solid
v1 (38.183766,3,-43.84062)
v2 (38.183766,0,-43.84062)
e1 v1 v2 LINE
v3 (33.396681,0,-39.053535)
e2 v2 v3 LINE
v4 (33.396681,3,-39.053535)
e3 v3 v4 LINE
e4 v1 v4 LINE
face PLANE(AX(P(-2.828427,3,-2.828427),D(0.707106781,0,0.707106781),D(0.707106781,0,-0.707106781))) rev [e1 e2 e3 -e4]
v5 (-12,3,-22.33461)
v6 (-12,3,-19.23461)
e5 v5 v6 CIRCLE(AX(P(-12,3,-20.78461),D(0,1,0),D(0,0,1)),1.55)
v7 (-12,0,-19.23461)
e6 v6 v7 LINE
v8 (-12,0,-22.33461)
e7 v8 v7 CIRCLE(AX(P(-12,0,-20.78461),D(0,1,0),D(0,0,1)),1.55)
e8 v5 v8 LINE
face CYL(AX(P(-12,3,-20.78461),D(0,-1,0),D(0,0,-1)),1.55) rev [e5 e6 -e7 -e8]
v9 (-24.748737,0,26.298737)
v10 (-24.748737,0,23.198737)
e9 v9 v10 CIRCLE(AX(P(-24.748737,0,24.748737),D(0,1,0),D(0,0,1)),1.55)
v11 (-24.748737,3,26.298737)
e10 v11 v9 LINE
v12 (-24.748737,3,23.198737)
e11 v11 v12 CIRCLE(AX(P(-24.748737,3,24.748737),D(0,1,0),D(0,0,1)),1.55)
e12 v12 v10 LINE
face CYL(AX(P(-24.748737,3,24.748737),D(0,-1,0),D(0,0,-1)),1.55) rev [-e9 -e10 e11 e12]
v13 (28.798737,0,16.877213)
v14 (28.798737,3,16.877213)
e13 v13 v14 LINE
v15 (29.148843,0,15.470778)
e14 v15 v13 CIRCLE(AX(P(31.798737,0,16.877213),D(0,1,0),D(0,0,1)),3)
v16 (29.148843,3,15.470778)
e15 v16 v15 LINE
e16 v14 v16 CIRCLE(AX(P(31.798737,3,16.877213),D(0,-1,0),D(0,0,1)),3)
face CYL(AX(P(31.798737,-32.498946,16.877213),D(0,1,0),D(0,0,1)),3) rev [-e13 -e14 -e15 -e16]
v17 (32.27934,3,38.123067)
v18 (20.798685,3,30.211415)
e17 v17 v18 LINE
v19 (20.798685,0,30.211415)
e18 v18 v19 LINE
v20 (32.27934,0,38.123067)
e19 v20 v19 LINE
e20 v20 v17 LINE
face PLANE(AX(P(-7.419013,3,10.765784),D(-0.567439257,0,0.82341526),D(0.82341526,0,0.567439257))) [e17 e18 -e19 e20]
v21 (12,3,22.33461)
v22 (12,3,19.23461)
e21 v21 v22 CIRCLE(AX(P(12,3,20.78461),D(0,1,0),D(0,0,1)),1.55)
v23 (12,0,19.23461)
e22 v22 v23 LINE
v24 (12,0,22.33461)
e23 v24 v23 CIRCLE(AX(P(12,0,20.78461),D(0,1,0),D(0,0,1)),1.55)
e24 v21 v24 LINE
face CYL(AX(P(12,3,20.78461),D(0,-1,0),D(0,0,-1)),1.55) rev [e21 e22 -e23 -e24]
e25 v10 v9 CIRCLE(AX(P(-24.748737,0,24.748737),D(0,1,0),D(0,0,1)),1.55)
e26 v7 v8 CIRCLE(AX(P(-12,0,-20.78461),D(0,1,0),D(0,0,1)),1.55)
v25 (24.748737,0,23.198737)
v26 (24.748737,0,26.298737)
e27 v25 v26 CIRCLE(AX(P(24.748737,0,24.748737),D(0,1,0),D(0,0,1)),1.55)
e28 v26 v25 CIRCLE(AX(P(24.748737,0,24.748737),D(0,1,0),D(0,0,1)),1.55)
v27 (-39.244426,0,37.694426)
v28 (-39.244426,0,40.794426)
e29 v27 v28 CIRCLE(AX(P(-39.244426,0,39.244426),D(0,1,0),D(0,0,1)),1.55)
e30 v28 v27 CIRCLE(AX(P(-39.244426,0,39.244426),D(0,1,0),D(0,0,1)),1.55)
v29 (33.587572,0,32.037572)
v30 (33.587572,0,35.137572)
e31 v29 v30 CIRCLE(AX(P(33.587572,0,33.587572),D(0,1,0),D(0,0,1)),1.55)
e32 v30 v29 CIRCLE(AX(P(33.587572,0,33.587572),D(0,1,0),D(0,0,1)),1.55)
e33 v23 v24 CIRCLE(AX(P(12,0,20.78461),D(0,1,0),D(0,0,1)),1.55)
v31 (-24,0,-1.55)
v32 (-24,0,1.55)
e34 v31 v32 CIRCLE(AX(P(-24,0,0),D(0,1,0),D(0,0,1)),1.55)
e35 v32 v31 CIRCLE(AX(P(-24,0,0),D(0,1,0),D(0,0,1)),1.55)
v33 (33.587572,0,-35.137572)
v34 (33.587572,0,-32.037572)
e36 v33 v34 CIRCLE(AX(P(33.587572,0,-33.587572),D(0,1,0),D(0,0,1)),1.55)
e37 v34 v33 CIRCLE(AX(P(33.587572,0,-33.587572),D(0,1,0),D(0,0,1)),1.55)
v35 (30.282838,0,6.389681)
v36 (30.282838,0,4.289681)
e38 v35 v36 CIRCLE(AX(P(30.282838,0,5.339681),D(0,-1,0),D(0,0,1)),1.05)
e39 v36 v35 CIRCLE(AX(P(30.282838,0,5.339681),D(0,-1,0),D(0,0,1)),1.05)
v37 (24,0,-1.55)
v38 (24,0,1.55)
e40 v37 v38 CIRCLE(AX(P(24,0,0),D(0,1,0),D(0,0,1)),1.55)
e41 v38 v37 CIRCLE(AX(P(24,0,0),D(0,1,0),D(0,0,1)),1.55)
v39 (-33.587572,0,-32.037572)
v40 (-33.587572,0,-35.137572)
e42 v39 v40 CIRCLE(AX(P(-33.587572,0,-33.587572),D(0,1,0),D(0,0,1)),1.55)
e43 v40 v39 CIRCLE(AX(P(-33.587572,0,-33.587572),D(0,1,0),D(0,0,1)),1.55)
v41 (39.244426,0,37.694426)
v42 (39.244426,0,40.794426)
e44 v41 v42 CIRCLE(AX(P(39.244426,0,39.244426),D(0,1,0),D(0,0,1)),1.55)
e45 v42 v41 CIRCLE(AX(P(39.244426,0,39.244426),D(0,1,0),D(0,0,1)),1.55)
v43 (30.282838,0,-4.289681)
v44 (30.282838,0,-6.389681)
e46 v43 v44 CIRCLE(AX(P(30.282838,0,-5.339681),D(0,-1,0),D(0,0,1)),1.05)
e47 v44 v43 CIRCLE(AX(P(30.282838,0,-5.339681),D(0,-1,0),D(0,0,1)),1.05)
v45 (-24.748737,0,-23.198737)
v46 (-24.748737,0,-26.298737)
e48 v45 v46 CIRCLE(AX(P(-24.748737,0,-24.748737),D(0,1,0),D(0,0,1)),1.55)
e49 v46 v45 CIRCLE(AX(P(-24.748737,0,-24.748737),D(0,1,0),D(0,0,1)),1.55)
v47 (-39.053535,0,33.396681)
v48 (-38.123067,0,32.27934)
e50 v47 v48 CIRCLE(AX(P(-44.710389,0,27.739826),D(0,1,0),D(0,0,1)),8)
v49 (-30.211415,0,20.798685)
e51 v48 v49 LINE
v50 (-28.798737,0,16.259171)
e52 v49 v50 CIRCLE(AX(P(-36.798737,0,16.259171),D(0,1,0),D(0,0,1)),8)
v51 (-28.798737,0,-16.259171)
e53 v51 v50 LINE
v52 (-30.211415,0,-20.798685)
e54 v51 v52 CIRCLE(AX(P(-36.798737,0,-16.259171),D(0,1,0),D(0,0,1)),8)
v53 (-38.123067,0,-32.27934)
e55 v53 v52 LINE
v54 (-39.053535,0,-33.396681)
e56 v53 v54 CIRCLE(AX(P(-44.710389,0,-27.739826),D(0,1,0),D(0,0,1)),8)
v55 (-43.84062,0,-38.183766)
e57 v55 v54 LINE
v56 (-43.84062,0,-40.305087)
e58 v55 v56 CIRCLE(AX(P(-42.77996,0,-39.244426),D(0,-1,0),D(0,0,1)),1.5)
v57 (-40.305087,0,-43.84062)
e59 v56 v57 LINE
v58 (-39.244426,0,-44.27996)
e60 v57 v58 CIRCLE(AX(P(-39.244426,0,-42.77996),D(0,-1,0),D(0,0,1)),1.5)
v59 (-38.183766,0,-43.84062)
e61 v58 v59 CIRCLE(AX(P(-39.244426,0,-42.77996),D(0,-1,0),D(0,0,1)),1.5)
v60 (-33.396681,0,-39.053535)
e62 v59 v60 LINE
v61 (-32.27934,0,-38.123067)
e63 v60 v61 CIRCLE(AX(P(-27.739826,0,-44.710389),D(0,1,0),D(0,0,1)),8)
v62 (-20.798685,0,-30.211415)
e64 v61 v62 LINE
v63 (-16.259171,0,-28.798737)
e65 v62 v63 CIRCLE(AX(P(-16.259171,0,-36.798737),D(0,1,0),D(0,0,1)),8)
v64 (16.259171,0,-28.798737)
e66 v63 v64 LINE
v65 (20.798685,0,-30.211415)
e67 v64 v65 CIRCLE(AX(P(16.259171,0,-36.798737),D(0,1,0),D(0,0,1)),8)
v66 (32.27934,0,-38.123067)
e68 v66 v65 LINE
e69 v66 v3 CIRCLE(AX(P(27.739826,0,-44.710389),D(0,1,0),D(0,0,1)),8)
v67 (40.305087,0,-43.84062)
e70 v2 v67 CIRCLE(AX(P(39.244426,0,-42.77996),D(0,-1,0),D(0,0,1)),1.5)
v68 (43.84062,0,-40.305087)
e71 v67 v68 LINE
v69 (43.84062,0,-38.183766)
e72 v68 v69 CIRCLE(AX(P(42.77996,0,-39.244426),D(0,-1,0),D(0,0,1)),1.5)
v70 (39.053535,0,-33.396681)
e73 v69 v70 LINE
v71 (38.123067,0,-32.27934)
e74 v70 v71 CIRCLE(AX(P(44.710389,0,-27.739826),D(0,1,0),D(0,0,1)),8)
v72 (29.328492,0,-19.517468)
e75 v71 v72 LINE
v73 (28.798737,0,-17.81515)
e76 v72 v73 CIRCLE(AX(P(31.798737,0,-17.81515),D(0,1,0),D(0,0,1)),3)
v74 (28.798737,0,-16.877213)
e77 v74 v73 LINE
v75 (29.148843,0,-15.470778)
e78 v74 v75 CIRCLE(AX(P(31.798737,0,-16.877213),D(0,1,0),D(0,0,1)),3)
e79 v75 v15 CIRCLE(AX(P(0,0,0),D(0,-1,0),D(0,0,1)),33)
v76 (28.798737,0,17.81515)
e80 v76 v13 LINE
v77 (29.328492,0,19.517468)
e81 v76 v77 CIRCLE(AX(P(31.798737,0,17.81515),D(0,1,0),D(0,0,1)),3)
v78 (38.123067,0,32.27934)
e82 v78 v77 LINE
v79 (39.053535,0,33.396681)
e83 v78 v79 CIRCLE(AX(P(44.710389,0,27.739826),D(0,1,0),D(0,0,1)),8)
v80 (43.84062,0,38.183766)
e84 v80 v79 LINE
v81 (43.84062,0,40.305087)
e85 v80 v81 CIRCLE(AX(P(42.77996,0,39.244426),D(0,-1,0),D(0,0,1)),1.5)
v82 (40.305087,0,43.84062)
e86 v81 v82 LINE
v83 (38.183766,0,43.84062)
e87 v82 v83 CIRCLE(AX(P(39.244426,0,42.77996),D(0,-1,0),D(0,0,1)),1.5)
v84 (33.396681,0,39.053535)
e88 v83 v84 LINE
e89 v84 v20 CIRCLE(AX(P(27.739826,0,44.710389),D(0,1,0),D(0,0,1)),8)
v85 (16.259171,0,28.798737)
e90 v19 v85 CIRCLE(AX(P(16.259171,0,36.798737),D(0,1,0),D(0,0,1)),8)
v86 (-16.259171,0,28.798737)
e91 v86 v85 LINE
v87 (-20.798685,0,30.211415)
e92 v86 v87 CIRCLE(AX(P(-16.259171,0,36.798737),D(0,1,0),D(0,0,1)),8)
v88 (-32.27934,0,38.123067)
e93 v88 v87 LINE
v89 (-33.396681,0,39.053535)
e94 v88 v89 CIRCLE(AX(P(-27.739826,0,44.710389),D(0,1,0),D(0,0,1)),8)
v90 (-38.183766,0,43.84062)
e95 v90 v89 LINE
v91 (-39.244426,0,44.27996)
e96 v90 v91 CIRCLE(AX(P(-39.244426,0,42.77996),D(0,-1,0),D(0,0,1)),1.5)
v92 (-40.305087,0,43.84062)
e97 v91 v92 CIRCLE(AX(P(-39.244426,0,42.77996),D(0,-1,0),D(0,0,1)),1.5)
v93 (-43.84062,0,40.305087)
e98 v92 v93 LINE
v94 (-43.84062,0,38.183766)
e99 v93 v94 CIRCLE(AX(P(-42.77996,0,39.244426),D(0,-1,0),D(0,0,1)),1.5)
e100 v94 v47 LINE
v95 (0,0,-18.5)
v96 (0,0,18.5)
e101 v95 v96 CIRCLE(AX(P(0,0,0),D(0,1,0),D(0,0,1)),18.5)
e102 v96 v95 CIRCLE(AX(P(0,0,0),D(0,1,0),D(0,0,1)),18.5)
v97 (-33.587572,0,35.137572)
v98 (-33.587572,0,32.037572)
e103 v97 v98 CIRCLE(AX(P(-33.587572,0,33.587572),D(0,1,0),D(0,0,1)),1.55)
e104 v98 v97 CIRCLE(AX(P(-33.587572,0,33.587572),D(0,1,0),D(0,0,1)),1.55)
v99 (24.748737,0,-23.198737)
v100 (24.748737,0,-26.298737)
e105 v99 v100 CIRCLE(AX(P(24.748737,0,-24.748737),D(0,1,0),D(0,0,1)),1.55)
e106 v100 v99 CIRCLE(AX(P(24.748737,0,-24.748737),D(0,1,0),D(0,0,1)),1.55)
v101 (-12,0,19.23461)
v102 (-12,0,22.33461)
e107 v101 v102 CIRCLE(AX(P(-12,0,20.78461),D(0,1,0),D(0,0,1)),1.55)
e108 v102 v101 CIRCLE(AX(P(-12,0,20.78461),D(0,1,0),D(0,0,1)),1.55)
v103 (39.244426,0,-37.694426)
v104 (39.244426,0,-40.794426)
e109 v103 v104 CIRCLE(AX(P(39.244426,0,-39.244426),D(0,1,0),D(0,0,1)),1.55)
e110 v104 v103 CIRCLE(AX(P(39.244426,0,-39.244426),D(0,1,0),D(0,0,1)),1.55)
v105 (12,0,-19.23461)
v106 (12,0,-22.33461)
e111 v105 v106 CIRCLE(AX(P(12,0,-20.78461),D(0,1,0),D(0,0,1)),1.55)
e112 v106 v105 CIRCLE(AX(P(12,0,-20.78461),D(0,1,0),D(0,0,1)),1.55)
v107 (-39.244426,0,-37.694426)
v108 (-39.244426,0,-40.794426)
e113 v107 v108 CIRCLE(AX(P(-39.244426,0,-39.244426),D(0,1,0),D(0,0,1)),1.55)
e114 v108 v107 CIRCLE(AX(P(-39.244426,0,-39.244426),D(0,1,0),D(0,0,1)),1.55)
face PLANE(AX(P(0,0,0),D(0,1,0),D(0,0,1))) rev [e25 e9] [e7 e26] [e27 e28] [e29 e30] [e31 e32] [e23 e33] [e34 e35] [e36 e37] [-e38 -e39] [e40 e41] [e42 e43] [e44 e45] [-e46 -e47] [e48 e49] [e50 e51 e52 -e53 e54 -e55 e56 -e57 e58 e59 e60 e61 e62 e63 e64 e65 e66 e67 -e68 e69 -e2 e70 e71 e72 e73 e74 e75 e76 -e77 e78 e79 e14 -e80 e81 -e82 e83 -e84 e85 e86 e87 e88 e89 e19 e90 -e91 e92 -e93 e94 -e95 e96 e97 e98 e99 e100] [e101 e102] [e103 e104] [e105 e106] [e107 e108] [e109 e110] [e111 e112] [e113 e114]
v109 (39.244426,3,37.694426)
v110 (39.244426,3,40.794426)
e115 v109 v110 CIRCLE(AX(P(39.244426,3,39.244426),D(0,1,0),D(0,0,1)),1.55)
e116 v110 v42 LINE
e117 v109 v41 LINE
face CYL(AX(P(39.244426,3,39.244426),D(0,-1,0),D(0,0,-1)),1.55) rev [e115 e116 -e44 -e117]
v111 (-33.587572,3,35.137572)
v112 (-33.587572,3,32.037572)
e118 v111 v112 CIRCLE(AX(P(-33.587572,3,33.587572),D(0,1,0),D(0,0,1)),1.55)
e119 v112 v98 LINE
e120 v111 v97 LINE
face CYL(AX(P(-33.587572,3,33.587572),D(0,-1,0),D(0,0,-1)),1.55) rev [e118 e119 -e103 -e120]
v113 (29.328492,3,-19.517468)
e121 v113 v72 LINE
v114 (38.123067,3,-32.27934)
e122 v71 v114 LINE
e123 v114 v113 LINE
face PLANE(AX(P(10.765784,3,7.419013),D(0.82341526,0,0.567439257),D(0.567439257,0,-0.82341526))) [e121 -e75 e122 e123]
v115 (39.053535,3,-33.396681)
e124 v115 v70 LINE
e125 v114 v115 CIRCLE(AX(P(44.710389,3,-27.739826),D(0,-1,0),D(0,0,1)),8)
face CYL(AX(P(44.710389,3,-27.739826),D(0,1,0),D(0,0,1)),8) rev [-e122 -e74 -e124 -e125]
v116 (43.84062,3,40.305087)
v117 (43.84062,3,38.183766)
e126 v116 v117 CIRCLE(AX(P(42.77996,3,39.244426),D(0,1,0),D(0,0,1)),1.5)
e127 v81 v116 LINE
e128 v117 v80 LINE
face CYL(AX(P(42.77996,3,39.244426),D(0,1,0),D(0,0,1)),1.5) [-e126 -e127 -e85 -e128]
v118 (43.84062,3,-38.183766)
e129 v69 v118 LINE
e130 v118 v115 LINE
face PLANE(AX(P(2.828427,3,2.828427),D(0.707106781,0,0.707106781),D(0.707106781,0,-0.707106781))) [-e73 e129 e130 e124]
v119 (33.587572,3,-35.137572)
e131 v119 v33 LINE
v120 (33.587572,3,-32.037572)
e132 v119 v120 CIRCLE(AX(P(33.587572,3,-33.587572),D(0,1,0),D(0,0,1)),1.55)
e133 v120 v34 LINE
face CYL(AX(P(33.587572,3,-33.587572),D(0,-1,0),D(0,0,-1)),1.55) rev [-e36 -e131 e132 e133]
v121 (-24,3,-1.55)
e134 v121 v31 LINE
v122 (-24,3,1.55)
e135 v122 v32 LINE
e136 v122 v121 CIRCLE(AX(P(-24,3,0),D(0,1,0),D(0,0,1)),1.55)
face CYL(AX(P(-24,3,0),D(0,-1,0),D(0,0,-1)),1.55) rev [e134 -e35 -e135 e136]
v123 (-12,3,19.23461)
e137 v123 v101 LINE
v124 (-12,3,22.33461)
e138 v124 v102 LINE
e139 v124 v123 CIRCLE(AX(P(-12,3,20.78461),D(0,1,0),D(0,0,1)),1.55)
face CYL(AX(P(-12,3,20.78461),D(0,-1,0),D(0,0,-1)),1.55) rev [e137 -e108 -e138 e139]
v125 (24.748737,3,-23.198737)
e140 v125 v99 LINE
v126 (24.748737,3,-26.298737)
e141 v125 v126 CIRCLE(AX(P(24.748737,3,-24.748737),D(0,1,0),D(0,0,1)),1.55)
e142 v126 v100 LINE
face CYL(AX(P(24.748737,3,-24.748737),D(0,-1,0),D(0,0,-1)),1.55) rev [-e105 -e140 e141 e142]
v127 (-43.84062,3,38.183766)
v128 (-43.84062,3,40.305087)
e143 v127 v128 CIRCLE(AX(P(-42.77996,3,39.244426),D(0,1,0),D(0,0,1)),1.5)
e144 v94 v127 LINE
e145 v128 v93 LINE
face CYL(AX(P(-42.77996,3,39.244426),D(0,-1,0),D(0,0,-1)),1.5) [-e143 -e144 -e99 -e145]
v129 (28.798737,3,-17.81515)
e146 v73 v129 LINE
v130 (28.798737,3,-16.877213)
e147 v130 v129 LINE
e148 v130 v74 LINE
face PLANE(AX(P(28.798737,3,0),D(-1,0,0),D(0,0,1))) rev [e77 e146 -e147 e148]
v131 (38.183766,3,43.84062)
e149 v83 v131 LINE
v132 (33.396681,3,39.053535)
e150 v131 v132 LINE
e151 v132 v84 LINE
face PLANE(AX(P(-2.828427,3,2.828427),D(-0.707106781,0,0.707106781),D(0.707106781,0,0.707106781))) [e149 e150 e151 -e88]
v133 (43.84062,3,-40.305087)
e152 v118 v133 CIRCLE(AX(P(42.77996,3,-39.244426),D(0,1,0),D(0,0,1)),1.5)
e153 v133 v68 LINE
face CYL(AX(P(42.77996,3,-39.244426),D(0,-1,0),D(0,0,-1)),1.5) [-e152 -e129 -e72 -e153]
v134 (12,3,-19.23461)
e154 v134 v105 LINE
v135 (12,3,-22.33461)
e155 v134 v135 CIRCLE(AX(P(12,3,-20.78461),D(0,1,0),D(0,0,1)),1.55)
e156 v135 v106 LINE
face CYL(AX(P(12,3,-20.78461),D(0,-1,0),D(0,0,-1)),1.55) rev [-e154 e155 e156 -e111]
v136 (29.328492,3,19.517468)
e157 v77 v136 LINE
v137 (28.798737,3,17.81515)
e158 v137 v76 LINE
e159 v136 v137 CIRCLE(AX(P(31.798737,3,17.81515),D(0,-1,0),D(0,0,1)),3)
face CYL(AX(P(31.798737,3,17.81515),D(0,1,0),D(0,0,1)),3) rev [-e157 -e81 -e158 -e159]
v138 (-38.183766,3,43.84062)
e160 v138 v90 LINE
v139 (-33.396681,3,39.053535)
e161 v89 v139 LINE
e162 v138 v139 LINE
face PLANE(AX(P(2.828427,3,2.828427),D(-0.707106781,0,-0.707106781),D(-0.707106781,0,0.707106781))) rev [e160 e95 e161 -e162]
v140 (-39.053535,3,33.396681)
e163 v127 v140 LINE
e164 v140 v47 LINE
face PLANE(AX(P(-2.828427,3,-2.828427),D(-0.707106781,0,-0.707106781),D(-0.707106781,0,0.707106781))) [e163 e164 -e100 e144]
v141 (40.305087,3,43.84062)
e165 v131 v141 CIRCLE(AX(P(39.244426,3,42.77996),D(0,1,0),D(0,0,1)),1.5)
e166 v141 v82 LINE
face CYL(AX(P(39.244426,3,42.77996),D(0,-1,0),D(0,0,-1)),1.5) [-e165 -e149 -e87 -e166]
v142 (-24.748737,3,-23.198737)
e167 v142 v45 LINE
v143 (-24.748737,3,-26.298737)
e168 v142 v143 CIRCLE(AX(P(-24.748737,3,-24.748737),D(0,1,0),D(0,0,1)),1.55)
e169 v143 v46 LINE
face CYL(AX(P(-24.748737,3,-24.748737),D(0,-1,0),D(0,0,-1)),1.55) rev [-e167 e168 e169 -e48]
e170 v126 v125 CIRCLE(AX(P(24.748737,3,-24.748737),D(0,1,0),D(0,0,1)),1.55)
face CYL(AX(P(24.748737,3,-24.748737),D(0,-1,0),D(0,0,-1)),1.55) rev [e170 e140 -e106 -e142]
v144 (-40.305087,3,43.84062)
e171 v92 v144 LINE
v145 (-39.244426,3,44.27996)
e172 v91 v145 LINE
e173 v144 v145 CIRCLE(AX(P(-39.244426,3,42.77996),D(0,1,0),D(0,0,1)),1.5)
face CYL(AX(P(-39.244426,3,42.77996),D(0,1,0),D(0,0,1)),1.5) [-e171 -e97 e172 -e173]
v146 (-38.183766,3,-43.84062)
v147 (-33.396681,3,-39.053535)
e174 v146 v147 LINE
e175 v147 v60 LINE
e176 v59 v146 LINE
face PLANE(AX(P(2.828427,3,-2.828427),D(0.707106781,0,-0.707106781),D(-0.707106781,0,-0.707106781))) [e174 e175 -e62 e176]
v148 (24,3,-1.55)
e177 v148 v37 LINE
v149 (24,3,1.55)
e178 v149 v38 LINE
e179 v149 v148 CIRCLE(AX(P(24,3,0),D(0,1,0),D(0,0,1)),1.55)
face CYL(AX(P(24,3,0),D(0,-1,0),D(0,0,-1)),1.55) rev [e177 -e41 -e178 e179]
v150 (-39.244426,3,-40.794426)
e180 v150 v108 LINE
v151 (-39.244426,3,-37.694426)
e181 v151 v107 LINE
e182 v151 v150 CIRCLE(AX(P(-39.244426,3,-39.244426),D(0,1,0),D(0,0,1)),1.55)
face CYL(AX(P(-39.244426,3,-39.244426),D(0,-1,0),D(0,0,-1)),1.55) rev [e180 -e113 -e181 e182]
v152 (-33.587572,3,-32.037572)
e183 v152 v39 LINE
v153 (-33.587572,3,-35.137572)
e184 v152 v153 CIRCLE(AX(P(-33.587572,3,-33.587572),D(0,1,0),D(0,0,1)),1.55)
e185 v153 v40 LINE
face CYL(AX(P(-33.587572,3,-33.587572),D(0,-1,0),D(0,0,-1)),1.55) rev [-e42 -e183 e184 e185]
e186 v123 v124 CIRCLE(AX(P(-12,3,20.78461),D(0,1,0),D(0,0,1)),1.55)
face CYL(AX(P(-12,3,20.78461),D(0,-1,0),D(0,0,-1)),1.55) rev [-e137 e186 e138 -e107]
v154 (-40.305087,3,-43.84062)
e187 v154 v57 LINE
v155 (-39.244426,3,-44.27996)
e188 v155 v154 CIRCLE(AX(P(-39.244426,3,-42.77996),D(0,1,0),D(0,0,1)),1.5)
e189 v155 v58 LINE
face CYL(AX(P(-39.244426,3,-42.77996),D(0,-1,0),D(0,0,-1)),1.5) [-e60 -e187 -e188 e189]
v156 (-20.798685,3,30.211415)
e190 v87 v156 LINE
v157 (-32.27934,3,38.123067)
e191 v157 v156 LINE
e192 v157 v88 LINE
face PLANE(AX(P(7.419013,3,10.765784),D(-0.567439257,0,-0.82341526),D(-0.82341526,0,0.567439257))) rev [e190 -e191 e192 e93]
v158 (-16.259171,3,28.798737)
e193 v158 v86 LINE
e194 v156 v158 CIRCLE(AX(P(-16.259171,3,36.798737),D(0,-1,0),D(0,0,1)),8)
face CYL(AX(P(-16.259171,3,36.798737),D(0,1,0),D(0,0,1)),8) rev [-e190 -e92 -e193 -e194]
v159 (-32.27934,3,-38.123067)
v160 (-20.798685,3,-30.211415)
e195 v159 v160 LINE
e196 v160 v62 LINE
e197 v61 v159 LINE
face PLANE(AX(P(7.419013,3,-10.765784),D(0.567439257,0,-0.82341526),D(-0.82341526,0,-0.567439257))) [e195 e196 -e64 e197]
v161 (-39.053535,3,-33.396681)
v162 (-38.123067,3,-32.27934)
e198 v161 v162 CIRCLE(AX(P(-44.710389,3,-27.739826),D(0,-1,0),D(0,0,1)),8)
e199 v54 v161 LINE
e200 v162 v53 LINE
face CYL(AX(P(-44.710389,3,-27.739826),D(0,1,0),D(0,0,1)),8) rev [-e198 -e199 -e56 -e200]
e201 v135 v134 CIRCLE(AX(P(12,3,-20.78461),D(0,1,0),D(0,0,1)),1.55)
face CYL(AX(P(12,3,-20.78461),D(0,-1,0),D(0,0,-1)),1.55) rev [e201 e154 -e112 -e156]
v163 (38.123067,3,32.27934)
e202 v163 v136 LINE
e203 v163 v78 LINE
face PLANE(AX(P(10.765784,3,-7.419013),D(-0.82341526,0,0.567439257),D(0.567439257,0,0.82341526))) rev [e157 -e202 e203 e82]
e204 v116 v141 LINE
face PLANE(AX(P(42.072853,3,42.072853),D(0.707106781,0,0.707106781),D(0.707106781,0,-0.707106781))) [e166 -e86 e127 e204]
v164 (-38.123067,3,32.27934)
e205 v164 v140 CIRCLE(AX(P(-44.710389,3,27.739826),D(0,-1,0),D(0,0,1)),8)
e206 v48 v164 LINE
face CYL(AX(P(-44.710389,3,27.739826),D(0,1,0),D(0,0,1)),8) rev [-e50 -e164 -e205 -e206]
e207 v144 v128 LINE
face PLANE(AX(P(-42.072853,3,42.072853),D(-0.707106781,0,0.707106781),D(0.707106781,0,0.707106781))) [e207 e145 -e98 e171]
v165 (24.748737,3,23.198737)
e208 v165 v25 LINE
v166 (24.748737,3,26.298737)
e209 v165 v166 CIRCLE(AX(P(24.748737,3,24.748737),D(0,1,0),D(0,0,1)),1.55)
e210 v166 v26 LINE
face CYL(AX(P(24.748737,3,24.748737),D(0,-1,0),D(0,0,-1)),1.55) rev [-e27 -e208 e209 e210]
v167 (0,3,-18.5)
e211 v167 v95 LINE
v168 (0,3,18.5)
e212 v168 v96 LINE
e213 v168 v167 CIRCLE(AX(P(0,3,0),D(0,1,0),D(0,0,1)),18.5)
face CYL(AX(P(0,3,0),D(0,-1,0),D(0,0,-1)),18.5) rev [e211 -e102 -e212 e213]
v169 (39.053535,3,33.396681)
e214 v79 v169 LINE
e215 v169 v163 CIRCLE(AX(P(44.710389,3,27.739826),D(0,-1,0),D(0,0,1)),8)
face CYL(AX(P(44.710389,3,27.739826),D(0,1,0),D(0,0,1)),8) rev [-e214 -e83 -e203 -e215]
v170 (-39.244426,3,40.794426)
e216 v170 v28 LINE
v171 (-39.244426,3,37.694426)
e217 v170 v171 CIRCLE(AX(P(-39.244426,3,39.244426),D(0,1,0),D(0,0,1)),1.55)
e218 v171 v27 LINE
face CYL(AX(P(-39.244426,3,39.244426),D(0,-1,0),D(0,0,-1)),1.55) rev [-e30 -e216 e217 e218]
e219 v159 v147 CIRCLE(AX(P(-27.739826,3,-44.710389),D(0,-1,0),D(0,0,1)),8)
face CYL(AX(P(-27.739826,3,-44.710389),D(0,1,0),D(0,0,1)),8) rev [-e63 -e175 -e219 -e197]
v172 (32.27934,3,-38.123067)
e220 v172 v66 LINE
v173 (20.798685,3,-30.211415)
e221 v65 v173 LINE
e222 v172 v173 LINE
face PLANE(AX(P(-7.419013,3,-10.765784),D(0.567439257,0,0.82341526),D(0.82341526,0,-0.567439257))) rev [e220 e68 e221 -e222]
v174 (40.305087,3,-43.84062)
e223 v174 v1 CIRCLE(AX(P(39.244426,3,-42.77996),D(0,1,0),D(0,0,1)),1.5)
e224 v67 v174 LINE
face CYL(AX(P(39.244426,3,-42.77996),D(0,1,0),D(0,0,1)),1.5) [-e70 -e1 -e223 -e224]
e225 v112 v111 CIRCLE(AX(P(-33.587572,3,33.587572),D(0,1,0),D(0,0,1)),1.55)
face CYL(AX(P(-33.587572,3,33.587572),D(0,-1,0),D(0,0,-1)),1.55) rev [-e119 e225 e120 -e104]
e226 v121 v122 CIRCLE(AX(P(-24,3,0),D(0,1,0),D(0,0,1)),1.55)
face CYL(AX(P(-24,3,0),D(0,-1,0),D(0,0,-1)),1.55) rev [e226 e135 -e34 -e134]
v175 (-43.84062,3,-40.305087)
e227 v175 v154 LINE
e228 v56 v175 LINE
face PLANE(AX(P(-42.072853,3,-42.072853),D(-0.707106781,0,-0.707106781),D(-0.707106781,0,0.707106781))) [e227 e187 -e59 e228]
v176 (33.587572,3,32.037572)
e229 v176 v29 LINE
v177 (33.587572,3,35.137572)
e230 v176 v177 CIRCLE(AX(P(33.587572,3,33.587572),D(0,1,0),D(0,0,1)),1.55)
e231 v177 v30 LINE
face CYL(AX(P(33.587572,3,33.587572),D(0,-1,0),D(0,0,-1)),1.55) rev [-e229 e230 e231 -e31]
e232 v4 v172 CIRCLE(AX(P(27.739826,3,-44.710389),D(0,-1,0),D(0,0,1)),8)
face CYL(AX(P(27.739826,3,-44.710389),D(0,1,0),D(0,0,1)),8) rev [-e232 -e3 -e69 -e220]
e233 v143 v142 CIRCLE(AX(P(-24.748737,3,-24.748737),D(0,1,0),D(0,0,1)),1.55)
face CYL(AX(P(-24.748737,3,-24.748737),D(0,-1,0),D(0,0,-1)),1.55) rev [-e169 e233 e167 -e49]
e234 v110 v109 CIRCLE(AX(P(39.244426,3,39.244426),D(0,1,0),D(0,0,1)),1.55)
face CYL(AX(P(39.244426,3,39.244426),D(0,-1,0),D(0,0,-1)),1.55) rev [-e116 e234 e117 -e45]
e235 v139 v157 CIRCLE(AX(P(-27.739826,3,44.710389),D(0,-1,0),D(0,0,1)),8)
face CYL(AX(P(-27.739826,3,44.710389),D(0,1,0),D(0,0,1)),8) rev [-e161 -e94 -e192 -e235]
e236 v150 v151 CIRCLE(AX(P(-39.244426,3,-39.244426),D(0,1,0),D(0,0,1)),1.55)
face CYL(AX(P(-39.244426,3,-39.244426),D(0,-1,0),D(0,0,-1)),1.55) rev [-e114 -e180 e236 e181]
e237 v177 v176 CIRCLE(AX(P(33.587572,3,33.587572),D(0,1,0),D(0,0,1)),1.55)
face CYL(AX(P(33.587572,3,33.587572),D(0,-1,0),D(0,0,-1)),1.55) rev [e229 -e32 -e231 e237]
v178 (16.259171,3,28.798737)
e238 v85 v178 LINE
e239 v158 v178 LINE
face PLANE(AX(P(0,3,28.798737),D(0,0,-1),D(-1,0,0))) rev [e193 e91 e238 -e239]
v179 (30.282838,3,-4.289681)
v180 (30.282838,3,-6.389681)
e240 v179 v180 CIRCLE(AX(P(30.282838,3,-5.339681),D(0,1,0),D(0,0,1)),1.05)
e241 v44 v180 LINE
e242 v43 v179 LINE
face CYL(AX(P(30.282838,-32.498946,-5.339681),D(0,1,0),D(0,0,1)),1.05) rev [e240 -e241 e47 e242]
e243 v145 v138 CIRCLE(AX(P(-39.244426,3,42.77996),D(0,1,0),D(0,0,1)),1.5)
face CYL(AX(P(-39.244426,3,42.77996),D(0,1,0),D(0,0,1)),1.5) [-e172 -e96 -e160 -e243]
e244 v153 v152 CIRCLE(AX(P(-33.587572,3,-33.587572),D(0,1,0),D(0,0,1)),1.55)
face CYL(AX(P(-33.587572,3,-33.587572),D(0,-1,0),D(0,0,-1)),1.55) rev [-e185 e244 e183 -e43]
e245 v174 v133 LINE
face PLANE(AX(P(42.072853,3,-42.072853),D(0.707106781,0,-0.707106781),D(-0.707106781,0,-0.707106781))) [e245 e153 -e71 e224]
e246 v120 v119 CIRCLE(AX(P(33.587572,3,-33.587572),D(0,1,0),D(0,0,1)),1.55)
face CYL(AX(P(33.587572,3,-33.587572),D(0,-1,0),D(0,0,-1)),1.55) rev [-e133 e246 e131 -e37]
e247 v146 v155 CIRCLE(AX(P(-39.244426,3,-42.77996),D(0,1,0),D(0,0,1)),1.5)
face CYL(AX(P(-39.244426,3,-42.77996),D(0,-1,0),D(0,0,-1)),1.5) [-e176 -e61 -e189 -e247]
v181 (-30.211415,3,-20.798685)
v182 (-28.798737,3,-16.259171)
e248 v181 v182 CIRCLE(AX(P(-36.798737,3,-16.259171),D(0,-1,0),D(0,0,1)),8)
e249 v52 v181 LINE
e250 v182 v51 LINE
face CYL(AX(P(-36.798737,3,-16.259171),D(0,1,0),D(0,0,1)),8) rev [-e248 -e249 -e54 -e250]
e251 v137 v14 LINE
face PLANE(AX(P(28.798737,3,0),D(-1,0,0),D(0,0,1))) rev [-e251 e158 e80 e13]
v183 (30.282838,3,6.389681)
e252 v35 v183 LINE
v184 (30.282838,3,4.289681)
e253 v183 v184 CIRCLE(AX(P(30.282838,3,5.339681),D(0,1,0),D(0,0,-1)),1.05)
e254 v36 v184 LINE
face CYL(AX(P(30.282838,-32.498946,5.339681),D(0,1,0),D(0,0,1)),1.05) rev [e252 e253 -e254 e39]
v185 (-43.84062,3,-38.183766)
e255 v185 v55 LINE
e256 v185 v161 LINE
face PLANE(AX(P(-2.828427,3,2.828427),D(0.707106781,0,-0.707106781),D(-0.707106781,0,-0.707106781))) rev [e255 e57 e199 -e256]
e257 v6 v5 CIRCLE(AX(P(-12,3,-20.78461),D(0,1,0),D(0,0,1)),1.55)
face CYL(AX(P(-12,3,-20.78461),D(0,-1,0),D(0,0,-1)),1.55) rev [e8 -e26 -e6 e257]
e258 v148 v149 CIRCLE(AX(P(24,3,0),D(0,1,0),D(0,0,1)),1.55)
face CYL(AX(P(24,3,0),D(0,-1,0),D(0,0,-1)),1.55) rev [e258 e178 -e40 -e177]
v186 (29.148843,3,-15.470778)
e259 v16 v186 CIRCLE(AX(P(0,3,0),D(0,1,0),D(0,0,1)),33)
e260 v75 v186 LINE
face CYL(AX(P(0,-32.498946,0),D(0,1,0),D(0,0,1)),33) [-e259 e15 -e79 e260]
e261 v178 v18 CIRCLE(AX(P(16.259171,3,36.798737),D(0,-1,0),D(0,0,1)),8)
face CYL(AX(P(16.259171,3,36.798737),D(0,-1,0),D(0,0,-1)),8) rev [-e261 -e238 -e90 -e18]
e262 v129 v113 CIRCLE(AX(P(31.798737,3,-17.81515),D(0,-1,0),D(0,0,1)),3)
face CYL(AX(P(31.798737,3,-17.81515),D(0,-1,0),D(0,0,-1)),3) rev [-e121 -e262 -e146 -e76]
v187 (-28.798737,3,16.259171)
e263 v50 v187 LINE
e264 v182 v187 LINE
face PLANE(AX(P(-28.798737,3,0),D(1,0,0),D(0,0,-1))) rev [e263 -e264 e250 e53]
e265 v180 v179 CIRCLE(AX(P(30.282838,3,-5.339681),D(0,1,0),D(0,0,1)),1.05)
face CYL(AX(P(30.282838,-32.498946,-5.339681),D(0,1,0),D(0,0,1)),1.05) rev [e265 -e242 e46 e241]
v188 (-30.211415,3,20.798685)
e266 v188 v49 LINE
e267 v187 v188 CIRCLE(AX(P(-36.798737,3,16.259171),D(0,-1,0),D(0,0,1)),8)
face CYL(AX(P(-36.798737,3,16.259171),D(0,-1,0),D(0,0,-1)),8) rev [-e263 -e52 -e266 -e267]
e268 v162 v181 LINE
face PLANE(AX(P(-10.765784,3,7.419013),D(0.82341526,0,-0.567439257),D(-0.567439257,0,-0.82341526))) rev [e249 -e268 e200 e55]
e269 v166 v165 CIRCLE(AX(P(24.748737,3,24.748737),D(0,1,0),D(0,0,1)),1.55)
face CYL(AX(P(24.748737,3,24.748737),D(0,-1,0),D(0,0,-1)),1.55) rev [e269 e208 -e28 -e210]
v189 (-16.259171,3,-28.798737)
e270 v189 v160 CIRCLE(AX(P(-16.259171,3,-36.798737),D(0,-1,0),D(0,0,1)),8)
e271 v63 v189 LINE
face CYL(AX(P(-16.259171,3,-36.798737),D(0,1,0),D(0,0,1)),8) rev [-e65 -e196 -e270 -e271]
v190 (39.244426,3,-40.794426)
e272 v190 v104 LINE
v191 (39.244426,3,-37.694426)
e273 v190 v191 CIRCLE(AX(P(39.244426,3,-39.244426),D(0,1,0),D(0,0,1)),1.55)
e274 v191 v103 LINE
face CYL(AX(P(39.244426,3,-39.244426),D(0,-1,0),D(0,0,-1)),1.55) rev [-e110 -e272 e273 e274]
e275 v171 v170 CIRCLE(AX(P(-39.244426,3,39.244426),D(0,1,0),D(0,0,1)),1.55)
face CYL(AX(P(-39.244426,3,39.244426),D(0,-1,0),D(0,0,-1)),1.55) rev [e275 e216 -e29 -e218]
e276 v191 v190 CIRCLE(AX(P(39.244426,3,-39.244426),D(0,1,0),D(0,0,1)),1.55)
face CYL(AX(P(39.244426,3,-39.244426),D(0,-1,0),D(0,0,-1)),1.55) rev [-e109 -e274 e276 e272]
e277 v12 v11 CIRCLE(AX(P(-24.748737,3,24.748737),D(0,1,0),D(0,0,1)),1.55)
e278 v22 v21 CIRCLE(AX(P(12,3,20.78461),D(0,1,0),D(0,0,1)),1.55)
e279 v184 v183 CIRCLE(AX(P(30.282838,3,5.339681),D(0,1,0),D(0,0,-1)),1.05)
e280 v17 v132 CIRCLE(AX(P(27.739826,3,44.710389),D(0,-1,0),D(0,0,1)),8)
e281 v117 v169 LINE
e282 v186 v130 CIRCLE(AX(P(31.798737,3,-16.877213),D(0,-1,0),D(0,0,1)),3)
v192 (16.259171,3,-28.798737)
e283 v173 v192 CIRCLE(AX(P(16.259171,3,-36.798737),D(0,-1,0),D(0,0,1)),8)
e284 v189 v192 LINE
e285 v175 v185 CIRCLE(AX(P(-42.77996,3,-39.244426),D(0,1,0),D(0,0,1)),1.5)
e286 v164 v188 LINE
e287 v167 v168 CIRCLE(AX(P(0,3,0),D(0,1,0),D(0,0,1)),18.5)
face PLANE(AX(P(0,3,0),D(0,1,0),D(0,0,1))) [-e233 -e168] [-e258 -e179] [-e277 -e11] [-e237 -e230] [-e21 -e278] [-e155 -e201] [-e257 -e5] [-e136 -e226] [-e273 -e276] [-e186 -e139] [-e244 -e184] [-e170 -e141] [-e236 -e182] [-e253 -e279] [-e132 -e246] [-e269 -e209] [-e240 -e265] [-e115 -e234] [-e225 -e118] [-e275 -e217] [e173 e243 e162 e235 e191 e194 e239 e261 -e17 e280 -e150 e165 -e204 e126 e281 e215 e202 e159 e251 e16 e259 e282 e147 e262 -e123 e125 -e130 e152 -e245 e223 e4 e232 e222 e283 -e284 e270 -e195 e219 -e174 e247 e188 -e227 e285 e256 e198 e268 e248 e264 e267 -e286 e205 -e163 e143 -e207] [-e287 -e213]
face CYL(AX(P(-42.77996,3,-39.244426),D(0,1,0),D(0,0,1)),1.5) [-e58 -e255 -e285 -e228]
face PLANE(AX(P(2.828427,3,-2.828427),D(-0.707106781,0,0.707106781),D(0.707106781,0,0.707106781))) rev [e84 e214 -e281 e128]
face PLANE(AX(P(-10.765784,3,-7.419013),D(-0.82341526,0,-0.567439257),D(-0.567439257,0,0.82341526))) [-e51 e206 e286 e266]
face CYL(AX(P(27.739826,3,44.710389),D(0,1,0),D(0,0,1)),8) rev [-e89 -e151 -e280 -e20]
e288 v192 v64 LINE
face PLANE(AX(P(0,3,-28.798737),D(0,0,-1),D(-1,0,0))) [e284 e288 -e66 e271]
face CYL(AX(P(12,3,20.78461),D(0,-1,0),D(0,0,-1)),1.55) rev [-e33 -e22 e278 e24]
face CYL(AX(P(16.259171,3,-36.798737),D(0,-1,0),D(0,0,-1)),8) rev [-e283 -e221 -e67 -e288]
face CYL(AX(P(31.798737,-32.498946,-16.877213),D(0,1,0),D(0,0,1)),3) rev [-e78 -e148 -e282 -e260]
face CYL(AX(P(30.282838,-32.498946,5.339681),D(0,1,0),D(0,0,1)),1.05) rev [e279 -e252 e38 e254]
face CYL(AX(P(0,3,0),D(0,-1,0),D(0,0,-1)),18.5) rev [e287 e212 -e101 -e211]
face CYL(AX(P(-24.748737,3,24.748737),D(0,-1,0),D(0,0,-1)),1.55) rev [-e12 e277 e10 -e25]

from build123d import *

# Parameters (mm, degrees)
SKETCH_1_R      = 1.55
SKETCH_1_R_2    = 18.5
EXTRUDE_1_DEPTH = 3
SKETCH_2_R      = 1.05
EXTRUDE_2_DEPTH = 3
FILLET_1_R      = 1.5
FILLET_2_R      = 8
FILLET_3_R      = 3


with BuildPart() as part:
    # 草图1 → 凸台-拉伸1 (new body)
    with BuildSketch(Plane(origin=(0, 0, 0), x_dir=(1, 0, 0), z_dir=(0, 1, 0))):
        Polygon((44.901280605, 39.244426356), (39.244426356, 44.901280605), (32.880465325, 38.537319575), (18.748737342, 28.798737342), (-18.748737342, 28.798737342), (-32.880465325, 38.537319575), (-39.244426356, 44.901280605), (-44.901280605, 39.244426356), (-38.537319575, 32.880465325), (-28.798737342, 18.748737342), (-28.798737342, -18.748737342), (-38.537319575, -32.880465325), (-44.901280605, -39.244426356), (-39.244426356, -44.901280605), (-32.880465325, -38.537319575), (-18.748737342, -28.798737342), (18.748737342, -28.798737342), (32.880465325, -38.537319575), (39.244426356, -44.901280605), (44.901280605, -39.244426356), (38.537319575, -32.880465325), (28.798737342, -18.748737342), (28.798737342, 18.748737342), (38.537319575, 32.880465325), align=None)
        with Locations(Location((-39.244426356, -39.244426356, 0), (0, 0, 270))):
            Circle(SKETCH_1_R, mode=Mode.SUBTRACT)
        with Locations(Location((-33.587572106, -33.587572106, 0), (0, 0, 270))):
            Circle(SKETCH_1_R, mode=Mode.SUBTRACT)
        with Locations(Location((-24.748737342, -24.748737342, 0), (0, 0, 270))):
            Circle(SKETCH_1_R, mode=Mode.SUBTRACT)
        with Locations(Location((-12, -20.784609691, 0), (0, 0, 270))):
            Circle(SKETCH_1_R, mode=Mode.SUBTRACT)
        with Locations(Location((39.244426356, -39.244426356, 0), (0, 0, 270))):
            Circle(SKETCH_1_R, mode=Mode.SUBTRACT)
        with Locations(Location((33.587572106, -33.587572106, 0), (0, 0, 270))):
            Circle(SKETCH_1_R, mode=Mode.SUBTRACT)
        with Locations(Location((24.748737342, -24.748737342, 0), (0, 0, 270))):
            Circle(SKETCH_1_R, mode=Mode.SUBTRACT)
        with Locations(Location((12, -20.784609691, 0), (0, 0, 270))):
            Circle(SKETCH_1_R, mode=Mode.SUBTRACT)
        with Locations(Location((-24, 0, 0), (0, 0, 270))):
            Circle(SKETCH_1_R, mode=Mode.SUBTRACT)
        with Locations(Location((-12, 20.784609691, 0), (0, 0, 270))):
            Circle(SKETCH_1_R, mode=Mode.SUBTRACT)
        with Locations(Location((-24.748737342, 24.748737342, 0), (0, 0, 270))):
            Circle(SKETCH_1_R, mode=Mode.SUBTRACT)
        with Locations(Location((-33.587572106, 33.587572106, 0), (0, 0, 270))):
            Circle(SKETCH_1_R, mode=Mode.SUBTRACT)
        with Locations(Location((-39.244426356, 39.244426356, 0), (0, 0, 270))):
            Circle(SKETCH_1_R, mode=Mode.SUBTRACT)
        with Locations(Location((0, 0, 0), (0, 0, 270))):
            Circle(SKETCH_1_R_2, mode=Mode.SUBTRACT)
        with Locations(Location((12, 20.784609691, 0), (0, 0, 270))):
            Circle(SKETCH_1_R, mode=Mode.SUBTRACT)
        with Locations(Location((24, 0, 0), (0, 0, 270))):
            Circle(SKETCH_1_R, mode=Mode.SUBTRACT)
        with Locations(Location((24.748737342, 24.748737342, 0), (0, 0, 270))):
            Circle(SKETCH_1_R, mode=Mode.SUBTRACT)
        with Locations(Location((33.587572106, 33.587572106, 0), (0, 0, 270))):
            Circle(SKETCH_1_R, mode=Mode.SUBTRACT)
        with Locations(Location((39.244426356, 39.244426356, 0), (0, 0, 270))):
            Circle(SKETCH_1_R, mode=Mode.SUBTRACT)
    extrude(amount=EXTRUDE_1_DEPTH)

    # 草图2 → 凸台-拉伸2 (add)
    with BuildSketch(Plane(origin=(0, 3, 0), x_dir=(1, 0, 0), z_dir=(0, 1, 0))):
        with BuildLine():
            Line((28.798737342, 16.113122836), (28.798737342, -16.113122836))
            ThreePointArc((28.798737342, -16.113122836), (33, 0), (28.798737342, 16.113122836))
        make_face()
        with Locations(Location((30.282838405, 5.339681463, 0), (0, 0, 270))):
            Circle(SKETCH_2_R, mode=Mode.SUBTRACT)
        with Locations(Location((30.282838405, -5.339681463, 0), (0, 0, 270))):
            Circle(SKETCH_2_R, mode=Mode.SUBTRACT)
    extrude(amount=-EXTRUDE_2_DEPTH)

    # 圆角1
    fillet_1_edges = [part.edges().sort_by_distance(p)[0] for p in [
        (39.244426356, 1.5, -44.901280605),
        (44.901280605, 1.5, -39.244426356),
        (44.901280605, 1.5, 39.244426356),
        (39.244426356, 1.5, 44.901280605),
        (-39.244426356, 1.5, 44.901280605),
        (-44.901280605, 1.5, 39.244426356),
        (-44.901280605, 1.5, -39.244426356),
        (-39.244426356, 1.5, -44.901280605),
    ]]
    fillet(fillet_1_edges, radius=FILLET_1_R)

    # 圆角2
    fillet_2_edges = [part.edges().sort_by_distance(p)[0] for p in [
        (18.748737342, 1.5, -28.798737342),
        (32.880465325, 1.5, -38.537319575),
        (38.537319575, 1.5, -32.880465325),
        (38.537319575, 1.5, 32.880465325),
        (32.880465325, 1.5, 38.537319575),
        (18.748737342, 1.5, 28.798737342),
        (-18.748737342, 1.5, 28.798737342),
        (-32.880465325, 1.5, 38.537319575),
        (-38.537319575, 1.5, 32.880465325),
        (-28.798737342, 1.5, 18.748737342),
        (-28.798737342, 1.5, -18.748737342),
        (-38.537319575, 1.5, -32.880465325),
        (-32.880465325, 1.5, -38.537319575),
        (-18.748737342, 1.5, -28.798737342),
    ]]
    fillet(fillet_2_edges, radius=FILLET_2_R)

    # 圆角3
    fillet_3_edges = [part.edges().sort_by_distance(p)[0] for p in [
        (28.798737342, 1.5, 16.113122836),
        (28.798737342, 1.5, -16.113122836),
        (28.798737342, 1.5, -18.748737342),
        (28.798737342, 1.5, 18.748737342),
    ]]
    fillet(fillet_3_edges, radius=FILLET_3_R)


solid = part.part
